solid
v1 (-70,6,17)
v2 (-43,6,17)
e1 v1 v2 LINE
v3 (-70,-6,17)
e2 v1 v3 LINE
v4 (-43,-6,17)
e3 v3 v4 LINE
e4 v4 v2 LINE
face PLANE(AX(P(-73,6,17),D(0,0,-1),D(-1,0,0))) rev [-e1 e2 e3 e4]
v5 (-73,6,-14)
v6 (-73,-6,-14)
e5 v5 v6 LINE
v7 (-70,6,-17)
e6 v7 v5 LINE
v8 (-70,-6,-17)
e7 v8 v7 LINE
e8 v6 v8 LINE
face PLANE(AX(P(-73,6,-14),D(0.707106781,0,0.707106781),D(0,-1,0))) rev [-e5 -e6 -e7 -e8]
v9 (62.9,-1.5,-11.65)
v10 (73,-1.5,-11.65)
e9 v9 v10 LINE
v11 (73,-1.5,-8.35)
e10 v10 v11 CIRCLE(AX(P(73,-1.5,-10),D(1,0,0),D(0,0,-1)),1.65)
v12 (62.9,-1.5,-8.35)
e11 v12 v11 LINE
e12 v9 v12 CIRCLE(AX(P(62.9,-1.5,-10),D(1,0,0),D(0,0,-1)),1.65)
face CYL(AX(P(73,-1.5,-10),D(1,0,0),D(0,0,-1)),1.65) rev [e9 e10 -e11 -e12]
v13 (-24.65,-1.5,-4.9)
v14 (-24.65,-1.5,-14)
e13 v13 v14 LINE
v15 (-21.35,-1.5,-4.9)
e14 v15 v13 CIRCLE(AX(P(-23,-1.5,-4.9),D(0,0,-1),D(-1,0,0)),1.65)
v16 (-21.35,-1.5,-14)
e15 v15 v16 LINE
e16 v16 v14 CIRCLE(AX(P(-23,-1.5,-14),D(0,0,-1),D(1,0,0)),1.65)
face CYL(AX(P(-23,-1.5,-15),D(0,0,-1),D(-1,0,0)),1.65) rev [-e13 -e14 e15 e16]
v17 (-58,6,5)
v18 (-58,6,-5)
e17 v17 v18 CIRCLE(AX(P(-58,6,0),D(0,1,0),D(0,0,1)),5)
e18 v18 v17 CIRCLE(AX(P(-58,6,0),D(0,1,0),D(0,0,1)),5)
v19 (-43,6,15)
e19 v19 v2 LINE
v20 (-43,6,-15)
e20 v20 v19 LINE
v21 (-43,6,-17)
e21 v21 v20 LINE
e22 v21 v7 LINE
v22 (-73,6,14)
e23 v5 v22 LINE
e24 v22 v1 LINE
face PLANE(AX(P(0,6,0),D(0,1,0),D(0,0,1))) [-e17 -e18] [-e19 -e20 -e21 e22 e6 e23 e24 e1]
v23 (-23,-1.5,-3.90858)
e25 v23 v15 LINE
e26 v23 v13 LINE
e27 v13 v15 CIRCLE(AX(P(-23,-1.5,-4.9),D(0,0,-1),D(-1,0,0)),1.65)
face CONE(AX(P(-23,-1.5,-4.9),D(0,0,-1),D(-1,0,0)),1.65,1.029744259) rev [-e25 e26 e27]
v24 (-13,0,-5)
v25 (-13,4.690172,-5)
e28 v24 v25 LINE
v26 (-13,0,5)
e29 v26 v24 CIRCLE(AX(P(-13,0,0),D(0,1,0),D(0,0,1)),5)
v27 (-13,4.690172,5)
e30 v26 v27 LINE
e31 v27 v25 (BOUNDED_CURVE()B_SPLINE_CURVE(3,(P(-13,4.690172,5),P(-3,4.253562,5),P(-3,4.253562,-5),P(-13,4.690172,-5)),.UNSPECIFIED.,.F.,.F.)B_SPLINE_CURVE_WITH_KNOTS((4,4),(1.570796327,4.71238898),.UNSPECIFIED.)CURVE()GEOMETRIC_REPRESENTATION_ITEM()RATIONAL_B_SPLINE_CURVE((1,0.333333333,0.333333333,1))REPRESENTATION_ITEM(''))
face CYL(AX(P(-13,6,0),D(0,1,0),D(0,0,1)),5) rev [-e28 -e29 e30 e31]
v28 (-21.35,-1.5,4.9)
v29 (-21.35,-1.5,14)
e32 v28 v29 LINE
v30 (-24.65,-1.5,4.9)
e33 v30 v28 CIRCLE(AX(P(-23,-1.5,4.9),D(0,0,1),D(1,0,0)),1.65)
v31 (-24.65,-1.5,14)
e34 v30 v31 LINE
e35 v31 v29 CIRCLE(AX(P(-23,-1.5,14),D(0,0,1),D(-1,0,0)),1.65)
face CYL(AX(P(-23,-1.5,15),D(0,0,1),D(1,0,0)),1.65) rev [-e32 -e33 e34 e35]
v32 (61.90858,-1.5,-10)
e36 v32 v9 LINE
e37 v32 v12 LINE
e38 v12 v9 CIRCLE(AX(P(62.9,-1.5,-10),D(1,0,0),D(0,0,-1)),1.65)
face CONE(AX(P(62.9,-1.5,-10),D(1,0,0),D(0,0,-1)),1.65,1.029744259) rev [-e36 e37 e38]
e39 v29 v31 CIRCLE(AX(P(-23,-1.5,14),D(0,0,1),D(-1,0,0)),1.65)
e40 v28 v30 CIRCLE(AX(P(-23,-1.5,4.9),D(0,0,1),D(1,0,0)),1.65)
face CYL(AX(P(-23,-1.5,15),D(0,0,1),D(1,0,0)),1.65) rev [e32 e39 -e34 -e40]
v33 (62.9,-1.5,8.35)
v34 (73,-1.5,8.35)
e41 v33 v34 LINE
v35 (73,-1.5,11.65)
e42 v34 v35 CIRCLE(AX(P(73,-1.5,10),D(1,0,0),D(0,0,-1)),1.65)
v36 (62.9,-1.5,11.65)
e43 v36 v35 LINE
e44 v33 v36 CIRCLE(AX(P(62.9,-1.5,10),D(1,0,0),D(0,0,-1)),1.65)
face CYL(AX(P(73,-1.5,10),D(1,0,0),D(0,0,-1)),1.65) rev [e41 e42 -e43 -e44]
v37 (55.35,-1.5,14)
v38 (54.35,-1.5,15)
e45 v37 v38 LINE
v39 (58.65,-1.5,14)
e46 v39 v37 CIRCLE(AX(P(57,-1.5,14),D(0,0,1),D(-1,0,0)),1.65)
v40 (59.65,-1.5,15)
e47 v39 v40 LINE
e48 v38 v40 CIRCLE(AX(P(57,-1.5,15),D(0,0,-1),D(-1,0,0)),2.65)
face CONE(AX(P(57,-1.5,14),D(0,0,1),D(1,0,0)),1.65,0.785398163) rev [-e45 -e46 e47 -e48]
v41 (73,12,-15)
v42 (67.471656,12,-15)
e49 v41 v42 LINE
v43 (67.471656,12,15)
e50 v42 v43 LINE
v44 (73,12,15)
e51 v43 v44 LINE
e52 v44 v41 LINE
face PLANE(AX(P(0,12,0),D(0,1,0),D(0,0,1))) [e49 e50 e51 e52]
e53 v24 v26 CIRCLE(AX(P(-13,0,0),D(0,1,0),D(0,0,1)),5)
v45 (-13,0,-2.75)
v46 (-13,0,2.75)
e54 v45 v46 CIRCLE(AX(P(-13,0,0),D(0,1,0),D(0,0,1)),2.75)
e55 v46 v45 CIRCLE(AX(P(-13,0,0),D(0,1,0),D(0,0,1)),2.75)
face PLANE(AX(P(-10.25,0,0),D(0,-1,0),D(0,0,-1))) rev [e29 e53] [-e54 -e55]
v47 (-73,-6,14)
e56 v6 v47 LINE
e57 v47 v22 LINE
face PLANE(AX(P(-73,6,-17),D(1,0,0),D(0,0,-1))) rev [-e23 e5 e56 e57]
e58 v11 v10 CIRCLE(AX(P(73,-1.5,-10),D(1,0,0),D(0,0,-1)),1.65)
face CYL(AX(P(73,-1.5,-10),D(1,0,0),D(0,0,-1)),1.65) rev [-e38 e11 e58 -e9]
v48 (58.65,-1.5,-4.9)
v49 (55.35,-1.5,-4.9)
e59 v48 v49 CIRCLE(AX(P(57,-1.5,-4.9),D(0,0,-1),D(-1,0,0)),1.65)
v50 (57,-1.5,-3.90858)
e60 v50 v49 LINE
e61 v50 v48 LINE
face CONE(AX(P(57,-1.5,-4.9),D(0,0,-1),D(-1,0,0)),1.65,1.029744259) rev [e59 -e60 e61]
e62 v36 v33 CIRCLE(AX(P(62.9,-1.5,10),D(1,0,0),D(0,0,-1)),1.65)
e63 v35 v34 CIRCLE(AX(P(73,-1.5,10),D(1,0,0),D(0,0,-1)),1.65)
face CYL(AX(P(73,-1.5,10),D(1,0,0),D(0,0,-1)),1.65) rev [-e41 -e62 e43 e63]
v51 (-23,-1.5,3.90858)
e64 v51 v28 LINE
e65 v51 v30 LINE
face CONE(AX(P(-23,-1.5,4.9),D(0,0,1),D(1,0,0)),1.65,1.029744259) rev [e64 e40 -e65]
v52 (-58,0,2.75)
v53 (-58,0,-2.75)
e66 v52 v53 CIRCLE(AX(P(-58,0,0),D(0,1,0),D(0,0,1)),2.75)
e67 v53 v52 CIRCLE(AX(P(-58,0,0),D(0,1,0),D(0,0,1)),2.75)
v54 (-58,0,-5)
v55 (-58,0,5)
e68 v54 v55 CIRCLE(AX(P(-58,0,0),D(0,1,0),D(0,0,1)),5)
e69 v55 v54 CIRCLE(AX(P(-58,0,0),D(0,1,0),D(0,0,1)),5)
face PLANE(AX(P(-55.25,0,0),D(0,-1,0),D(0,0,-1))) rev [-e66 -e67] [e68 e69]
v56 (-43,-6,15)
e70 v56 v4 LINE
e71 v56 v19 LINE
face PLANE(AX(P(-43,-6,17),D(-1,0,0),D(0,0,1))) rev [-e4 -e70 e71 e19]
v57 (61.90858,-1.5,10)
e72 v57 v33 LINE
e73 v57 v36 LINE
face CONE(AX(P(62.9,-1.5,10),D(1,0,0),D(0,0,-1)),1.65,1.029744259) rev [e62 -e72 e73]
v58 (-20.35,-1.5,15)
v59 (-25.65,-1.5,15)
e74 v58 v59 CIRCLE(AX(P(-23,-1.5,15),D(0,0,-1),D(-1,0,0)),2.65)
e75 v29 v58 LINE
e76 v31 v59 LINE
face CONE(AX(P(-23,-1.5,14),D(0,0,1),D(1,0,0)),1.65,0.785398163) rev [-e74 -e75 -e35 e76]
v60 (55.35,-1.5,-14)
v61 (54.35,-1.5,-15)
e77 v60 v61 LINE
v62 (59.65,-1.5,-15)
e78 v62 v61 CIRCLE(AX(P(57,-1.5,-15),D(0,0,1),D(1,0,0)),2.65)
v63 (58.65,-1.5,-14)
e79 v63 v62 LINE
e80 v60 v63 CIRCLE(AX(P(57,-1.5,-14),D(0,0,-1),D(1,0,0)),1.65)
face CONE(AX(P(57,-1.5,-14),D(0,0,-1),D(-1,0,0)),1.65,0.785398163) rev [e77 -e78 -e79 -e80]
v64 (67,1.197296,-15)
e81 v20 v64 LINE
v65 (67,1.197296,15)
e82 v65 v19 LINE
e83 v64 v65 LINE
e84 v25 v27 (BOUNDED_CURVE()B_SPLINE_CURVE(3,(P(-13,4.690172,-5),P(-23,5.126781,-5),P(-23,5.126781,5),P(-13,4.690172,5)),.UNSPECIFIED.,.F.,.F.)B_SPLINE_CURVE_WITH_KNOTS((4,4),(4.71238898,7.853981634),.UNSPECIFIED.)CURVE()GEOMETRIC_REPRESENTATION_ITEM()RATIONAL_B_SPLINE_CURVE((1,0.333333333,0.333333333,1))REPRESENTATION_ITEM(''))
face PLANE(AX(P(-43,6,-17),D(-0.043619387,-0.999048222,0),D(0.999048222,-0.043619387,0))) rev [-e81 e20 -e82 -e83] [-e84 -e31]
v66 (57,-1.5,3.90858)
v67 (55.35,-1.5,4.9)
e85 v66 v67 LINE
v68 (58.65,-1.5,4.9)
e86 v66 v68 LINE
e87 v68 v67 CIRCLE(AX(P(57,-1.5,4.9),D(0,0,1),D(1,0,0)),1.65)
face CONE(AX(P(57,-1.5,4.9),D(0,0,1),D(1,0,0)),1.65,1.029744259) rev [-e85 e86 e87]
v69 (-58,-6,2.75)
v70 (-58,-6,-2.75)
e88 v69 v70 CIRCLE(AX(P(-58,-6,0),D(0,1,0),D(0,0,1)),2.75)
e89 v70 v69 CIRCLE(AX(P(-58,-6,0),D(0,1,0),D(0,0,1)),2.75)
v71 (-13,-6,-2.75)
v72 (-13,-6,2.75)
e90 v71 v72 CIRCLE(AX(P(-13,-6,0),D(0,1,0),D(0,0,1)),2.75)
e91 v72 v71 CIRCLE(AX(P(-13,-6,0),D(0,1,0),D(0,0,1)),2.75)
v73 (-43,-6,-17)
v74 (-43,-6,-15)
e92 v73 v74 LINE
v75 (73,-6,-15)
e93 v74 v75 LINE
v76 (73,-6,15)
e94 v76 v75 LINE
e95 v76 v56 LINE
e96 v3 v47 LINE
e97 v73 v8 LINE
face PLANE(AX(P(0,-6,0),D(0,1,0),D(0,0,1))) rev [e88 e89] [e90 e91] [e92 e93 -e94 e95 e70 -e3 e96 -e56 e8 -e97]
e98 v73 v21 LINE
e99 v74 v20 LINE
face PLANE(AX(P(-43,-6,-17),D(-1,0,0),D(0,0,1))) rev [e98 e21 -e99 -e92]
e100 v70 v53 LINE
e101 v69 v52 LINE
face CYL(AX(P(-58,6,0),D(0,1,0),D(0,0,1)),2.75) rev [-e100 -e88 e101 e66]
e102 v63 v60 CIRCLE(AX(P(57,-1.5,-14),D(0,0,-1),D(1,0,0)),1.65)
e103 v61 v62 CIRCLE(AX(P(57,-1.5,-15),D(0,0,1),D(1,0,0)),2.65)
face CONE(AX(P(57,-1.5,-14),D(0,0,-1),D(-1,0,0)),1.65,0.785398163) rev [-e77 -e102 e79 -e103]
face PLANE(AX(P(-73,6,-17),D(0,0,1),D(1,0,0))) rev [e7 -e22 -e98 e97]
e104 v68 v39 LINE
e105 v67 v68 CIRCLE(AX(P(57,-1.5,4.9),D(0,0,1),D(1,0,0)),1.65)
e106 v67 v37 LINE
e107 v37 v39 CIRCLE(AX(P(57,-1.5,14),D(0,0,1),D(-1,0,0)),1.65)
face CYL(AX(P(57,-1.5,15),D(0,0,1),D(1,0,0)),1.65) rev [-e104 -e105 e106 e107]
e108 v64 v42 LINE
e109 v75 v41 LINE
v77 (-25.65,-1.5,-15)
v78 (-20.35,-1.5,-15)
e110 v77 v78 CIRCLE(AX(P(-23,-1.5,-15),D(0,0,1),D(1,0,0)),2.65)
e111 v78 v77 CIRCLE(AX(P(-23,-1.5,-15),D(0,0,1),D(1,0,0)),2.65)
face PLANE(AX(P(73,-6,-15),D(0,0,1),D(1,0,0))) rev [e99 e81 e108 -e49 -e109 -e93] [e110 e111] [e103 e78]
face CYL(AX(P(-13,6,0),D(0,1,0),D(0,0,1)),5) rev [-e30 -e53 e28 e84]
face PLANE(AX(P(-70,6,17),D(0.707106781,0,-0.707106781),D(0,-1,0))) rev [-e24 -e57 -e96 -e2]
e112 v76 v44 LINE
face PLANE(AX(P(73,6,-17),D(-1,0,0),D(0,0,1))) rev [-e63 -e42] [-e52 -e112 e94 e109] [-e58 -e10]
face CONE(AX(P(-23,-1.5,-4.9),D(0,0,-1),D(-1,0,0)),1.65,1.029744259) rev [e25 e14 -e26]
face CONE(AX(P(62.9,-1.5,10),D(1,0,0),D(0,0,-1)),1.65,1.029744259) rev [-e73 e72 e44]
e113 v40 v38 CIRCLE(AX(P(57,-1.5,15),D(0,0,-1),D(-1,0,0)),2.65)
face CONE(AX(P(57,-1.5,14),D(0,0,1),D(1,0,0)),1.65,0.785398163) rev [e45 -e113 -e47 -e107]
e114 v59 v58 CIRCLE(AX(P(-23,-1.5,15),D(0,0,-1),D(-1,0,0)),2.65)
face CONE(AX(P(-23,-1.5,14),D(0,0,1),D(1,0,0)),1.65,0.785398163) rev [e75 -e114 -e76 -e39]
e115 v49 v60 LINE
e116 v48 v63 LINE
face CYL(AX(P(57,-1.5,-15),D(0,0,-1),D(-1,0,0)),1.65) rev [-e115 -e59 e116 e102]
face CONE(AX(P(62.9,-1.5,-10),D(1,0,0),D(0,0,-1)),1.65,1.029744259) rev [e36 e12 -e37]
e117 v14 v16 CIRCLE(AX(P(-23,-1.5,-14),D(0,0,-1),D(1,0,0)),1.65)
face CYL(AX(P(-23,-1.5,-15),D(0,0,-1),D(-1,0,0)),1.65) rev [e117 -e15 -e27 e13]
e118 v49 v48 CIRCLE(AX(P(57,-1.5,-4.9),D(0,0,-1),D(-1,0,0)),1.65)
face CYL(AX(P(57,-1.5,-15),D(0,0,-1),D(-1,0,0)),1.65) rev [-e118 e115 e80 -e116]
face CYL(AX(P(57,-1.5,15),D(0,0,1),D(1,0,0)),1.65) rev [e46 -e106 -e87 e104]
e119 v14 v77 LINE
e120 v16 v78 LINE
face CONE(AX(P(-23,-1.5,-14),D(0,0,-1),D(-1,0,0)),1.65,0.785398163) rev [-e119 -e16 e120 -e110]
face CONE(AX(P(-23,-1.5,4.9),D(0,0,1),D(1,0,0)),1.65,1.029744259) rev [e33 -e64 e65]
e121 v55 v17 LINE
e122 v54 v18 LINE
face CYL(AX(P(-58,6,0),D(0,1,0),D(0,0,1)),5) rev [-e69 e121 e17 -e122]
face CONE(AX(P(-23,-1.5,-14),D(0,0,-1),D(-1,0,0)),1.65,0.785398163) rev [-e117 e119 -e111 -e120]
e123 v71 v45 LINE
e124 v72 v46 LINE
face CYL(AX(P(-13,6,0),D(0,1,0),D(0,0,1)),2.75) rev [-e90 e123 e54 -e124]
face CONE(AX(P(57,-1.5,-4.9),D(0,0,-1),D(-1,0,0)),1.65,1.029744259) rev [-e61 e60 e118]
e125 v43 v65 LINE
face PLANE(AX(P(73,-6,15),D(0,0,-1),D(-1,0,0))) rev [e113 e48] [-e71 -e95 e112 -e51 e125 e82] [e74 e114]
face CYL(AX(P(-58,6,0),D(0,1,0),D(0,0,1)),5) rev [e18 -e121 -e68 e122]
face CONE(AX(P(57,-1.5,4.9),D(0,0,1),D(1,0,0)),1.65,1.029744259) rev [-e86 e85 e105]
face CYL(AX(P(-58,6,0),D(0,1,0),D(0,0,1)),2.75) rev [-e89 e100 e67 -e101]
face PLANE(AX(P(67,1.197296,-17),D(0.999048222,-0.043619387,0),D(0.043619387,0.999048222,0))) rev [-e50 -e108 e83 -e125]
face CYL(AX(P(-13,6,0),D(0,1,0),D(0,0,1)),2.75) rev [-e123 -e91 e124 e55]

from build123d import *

# Parameters (mm, degrees)
SKETCH1_W                                            = 146
SKETCH1_H                                            = 34
BOSS_EXTRUDE1_DEPTH                                  = 6
HOLE_SIZE_PER_SOCKET_HEAD_CAP_SCREW_TYPE_D           = 5.5
HOLE_SIZE_PER_SOCKET_HEAD_CAP_SCREW_TYPE_CBORE_D     = 10
HOLE_SIZE_PER_SOCKET_HEAD_CAP_SCREW_TYPE_CBORE_DEPTH = 6
M4_TAPPED_HOLE2_D                                    = 3.3
M4_TAPPED_HOLE2_DEPTH                                = 10.1
M4_TAPPED_HOLE2_TIP                                  = 0.991420021
CHAMFER1_SIZE                                        = 3
SKETCH8_W                                            = 116
SKETCH8_H                                            = 2
CUT_EXTRUDE1_DEPTH                                   = 76.907838857
M4_TAPPED_HOLE3_AT_2_COUNT                           = 2
M4_TAPPED_HOLE3_AT_2_PITCH                           = 80
SKETCH11_W                                           = 6
SKETCH11_H                                           = 30
BOSS_EXTRUDE2_DEPTH                                  = 6
CUT_EXTRUDE2_DEPTH                                   = 82.418671077
CUT_EXTRUDE3_DEPTH                                   = 82.418671077
CHAMFER2_SIZE                                        = 1


with BuildPart() as part:
    # Sketch1 → Boss-Extrude1 (new, symmetric)
    with BuildSketch(Plane(origin=(0, 0, 0), x_dir=(1, 0, 0), z_dir=(0, 1, 0))):
        Rectangle(SKETCH1_W, SKETCH1_H)
    extrude(amount=BOSS_EXTRUDE1_DEPTH, both=True)

    # Hole size per socket head cap screw type1 (through all)
    with Locations(Plane(origin=(0, 6, 0), x_dir=(1, 0, 0), z_dir=(0, 1, 0))):
        with Locations((-58, 0), (-13, 0)):
            CounterBoreHole(HOLE_SIZE_PER_SOCKET_HEAD_CAP_SCREW_TYPE_D / 2, HOLE_SIZE_PER_SOCKET_HEAD_CAP_SCREW_TYPE_CBORE_D / 2, HOLE_SIZE_PER_SOCKET_HEAD_CAP_SCREW_TYPE_CBORE_DEPTH)

    # M4 Tapped Hole2
    with Locations(Plane(origin=(73, 0, 0), x_dir=(0, 0, -1), z_dir=(1, 0, 0))):
        with Locations((-10, -1.5), (10, -1.5)):
            Hole(M4_TAPPED_HOLE2_D / 2, depth=M4_TAPPED_HOLE2_DEPTH)
            with Locations((0, 0, -(M4_TAPPED_HOLE2_DEPTH + M4_TAPPED_HOLE2_TIP / 2))):  # 118° drill point
                Cone(0, M4_TAPPED_HOLE2_D / 2, M4_TAPPED_HOLE2_TIP, mode=Mode.SUBTRACT)

    # Chamfer1
    chamfer1_edges = [part.edges().sort_by_distance(p)[0] for p in [
        (-73, 0, 17),
        (-73, 0, -17),
    ]]
    chamfer(chamfer1_edges, length=CHAMFER1_SIZE)

    # Sketch8 → Cut-Extrude1 (cut, through all)
    with BuildSketch(Plane(origin=(0, 6, 0), x_dir=(1, 0, 0), z_dir=(0, 1, 0))):
        with Locations((15, -16)):
            Rectangle(SKETCH8_W, SKETCH8_H)
        with Locations((15, 16)):
            Rectangle(SKETCH8_W, SKETCH8_H)
    extrude(amount=-CUT_EXTRUDE1_DEPTH, mode=Mode.SUBTRACT)

    # Sketch9 → M4 Tapped Hole3 (revolve, cut)
    with BuildSketch(Plane(origin=(-23, -1.5, 15), x_dir=(0, -1, 0), z_dir=(1, 0, 0))):
        Polygon((0, 0), (0, 11.091420021), (1.65, 10.1), (1.65, 0), align=None)
    m4_tapped_hole3 = revolve(axis=Axis((-23, -1.5, 21.35), (0, 0, -1)), mode=Mode.SUBTRACT)

    # M4 Tapped Hole3 at 2: M4 Tapped Hole3 ×2
    with Locations(*[(i * M4_TAPPED_HOLE3_AT_2_PITCH, 0, 0) for i in range(1, M4_TAPPED_HOLE3_AT_2_COUNT)]):
        add(m4_tapped_hole3, mode=Mode.SUBTRACT)

    # Mirror1: M4 Tapped Hole3 across plane
    add(m4_tapped_hole3.mirror(Plane.XY), mode=Mode.SUBTRACT)

    # Mirror1 copy 1 sketch → Mirror1 copy 1 (revolve, cut)
    with BuildSketch(Plane(origin=(57, -1.5, -15), x_dir=(0, -1, 0), z_dir=(1, 0, 0))):
        Polygon((0, 0), (0, -11.091420021), (1.65, -10.1), (1.65, 0), align=None)
    revolve(axis=Axis((57, -1.5, -21.35), (0, 0, -1)), mode=Mode.SUBTRACT)

    # Sketch11 → Boss-Extrude2 (add)
    with BuildSketch(Plane(origin=(0, 6, 0), x_dir=(1, 0, 0), z_dir=(0, 1, 0))):
        with Locations((70, 0)):
            Rectangle(SKETCH11_W, SKETCH11_H)
    extrude(amount=BOSS_EXTRUDE2_DEPTH)

    # Sketch12 → Cut-Extrude2 (cut, through all)
    with BuildSketch(Plane.XY.offset(17)):
        Polygon((67, 6), (-43, 6), (67, 1.19729628), align=None)
    extrude(amount=-CUT_EXTRUDE2_DEPTH, mode=Mode.SUBTRACT)

    # Sketch13 → Cut-Extrude3 (cut, through all)
    with BuildSketch(Plane.XY.offset(17)):
        Polygon((67, 12), (67, 1.19729628), (67.47165623, 12), align=None)
    extrude(amount=-CUT_EXTRUDE3_DEPTH, mode=Mode.SUBTRACT)

    # Chamfer2
    chamfer2_edges = [part.edges().sort_by_distance(p)[0] for p in [
        (57, 0.15, 15),
        (-23, 0.15, 15),
        (57, 0.15, -15),
        (-23, 0.15, -15),
    ]]
    chamfer(chamfer2_edges, length=CHAMFER2_SIZE)


solid = part.part
